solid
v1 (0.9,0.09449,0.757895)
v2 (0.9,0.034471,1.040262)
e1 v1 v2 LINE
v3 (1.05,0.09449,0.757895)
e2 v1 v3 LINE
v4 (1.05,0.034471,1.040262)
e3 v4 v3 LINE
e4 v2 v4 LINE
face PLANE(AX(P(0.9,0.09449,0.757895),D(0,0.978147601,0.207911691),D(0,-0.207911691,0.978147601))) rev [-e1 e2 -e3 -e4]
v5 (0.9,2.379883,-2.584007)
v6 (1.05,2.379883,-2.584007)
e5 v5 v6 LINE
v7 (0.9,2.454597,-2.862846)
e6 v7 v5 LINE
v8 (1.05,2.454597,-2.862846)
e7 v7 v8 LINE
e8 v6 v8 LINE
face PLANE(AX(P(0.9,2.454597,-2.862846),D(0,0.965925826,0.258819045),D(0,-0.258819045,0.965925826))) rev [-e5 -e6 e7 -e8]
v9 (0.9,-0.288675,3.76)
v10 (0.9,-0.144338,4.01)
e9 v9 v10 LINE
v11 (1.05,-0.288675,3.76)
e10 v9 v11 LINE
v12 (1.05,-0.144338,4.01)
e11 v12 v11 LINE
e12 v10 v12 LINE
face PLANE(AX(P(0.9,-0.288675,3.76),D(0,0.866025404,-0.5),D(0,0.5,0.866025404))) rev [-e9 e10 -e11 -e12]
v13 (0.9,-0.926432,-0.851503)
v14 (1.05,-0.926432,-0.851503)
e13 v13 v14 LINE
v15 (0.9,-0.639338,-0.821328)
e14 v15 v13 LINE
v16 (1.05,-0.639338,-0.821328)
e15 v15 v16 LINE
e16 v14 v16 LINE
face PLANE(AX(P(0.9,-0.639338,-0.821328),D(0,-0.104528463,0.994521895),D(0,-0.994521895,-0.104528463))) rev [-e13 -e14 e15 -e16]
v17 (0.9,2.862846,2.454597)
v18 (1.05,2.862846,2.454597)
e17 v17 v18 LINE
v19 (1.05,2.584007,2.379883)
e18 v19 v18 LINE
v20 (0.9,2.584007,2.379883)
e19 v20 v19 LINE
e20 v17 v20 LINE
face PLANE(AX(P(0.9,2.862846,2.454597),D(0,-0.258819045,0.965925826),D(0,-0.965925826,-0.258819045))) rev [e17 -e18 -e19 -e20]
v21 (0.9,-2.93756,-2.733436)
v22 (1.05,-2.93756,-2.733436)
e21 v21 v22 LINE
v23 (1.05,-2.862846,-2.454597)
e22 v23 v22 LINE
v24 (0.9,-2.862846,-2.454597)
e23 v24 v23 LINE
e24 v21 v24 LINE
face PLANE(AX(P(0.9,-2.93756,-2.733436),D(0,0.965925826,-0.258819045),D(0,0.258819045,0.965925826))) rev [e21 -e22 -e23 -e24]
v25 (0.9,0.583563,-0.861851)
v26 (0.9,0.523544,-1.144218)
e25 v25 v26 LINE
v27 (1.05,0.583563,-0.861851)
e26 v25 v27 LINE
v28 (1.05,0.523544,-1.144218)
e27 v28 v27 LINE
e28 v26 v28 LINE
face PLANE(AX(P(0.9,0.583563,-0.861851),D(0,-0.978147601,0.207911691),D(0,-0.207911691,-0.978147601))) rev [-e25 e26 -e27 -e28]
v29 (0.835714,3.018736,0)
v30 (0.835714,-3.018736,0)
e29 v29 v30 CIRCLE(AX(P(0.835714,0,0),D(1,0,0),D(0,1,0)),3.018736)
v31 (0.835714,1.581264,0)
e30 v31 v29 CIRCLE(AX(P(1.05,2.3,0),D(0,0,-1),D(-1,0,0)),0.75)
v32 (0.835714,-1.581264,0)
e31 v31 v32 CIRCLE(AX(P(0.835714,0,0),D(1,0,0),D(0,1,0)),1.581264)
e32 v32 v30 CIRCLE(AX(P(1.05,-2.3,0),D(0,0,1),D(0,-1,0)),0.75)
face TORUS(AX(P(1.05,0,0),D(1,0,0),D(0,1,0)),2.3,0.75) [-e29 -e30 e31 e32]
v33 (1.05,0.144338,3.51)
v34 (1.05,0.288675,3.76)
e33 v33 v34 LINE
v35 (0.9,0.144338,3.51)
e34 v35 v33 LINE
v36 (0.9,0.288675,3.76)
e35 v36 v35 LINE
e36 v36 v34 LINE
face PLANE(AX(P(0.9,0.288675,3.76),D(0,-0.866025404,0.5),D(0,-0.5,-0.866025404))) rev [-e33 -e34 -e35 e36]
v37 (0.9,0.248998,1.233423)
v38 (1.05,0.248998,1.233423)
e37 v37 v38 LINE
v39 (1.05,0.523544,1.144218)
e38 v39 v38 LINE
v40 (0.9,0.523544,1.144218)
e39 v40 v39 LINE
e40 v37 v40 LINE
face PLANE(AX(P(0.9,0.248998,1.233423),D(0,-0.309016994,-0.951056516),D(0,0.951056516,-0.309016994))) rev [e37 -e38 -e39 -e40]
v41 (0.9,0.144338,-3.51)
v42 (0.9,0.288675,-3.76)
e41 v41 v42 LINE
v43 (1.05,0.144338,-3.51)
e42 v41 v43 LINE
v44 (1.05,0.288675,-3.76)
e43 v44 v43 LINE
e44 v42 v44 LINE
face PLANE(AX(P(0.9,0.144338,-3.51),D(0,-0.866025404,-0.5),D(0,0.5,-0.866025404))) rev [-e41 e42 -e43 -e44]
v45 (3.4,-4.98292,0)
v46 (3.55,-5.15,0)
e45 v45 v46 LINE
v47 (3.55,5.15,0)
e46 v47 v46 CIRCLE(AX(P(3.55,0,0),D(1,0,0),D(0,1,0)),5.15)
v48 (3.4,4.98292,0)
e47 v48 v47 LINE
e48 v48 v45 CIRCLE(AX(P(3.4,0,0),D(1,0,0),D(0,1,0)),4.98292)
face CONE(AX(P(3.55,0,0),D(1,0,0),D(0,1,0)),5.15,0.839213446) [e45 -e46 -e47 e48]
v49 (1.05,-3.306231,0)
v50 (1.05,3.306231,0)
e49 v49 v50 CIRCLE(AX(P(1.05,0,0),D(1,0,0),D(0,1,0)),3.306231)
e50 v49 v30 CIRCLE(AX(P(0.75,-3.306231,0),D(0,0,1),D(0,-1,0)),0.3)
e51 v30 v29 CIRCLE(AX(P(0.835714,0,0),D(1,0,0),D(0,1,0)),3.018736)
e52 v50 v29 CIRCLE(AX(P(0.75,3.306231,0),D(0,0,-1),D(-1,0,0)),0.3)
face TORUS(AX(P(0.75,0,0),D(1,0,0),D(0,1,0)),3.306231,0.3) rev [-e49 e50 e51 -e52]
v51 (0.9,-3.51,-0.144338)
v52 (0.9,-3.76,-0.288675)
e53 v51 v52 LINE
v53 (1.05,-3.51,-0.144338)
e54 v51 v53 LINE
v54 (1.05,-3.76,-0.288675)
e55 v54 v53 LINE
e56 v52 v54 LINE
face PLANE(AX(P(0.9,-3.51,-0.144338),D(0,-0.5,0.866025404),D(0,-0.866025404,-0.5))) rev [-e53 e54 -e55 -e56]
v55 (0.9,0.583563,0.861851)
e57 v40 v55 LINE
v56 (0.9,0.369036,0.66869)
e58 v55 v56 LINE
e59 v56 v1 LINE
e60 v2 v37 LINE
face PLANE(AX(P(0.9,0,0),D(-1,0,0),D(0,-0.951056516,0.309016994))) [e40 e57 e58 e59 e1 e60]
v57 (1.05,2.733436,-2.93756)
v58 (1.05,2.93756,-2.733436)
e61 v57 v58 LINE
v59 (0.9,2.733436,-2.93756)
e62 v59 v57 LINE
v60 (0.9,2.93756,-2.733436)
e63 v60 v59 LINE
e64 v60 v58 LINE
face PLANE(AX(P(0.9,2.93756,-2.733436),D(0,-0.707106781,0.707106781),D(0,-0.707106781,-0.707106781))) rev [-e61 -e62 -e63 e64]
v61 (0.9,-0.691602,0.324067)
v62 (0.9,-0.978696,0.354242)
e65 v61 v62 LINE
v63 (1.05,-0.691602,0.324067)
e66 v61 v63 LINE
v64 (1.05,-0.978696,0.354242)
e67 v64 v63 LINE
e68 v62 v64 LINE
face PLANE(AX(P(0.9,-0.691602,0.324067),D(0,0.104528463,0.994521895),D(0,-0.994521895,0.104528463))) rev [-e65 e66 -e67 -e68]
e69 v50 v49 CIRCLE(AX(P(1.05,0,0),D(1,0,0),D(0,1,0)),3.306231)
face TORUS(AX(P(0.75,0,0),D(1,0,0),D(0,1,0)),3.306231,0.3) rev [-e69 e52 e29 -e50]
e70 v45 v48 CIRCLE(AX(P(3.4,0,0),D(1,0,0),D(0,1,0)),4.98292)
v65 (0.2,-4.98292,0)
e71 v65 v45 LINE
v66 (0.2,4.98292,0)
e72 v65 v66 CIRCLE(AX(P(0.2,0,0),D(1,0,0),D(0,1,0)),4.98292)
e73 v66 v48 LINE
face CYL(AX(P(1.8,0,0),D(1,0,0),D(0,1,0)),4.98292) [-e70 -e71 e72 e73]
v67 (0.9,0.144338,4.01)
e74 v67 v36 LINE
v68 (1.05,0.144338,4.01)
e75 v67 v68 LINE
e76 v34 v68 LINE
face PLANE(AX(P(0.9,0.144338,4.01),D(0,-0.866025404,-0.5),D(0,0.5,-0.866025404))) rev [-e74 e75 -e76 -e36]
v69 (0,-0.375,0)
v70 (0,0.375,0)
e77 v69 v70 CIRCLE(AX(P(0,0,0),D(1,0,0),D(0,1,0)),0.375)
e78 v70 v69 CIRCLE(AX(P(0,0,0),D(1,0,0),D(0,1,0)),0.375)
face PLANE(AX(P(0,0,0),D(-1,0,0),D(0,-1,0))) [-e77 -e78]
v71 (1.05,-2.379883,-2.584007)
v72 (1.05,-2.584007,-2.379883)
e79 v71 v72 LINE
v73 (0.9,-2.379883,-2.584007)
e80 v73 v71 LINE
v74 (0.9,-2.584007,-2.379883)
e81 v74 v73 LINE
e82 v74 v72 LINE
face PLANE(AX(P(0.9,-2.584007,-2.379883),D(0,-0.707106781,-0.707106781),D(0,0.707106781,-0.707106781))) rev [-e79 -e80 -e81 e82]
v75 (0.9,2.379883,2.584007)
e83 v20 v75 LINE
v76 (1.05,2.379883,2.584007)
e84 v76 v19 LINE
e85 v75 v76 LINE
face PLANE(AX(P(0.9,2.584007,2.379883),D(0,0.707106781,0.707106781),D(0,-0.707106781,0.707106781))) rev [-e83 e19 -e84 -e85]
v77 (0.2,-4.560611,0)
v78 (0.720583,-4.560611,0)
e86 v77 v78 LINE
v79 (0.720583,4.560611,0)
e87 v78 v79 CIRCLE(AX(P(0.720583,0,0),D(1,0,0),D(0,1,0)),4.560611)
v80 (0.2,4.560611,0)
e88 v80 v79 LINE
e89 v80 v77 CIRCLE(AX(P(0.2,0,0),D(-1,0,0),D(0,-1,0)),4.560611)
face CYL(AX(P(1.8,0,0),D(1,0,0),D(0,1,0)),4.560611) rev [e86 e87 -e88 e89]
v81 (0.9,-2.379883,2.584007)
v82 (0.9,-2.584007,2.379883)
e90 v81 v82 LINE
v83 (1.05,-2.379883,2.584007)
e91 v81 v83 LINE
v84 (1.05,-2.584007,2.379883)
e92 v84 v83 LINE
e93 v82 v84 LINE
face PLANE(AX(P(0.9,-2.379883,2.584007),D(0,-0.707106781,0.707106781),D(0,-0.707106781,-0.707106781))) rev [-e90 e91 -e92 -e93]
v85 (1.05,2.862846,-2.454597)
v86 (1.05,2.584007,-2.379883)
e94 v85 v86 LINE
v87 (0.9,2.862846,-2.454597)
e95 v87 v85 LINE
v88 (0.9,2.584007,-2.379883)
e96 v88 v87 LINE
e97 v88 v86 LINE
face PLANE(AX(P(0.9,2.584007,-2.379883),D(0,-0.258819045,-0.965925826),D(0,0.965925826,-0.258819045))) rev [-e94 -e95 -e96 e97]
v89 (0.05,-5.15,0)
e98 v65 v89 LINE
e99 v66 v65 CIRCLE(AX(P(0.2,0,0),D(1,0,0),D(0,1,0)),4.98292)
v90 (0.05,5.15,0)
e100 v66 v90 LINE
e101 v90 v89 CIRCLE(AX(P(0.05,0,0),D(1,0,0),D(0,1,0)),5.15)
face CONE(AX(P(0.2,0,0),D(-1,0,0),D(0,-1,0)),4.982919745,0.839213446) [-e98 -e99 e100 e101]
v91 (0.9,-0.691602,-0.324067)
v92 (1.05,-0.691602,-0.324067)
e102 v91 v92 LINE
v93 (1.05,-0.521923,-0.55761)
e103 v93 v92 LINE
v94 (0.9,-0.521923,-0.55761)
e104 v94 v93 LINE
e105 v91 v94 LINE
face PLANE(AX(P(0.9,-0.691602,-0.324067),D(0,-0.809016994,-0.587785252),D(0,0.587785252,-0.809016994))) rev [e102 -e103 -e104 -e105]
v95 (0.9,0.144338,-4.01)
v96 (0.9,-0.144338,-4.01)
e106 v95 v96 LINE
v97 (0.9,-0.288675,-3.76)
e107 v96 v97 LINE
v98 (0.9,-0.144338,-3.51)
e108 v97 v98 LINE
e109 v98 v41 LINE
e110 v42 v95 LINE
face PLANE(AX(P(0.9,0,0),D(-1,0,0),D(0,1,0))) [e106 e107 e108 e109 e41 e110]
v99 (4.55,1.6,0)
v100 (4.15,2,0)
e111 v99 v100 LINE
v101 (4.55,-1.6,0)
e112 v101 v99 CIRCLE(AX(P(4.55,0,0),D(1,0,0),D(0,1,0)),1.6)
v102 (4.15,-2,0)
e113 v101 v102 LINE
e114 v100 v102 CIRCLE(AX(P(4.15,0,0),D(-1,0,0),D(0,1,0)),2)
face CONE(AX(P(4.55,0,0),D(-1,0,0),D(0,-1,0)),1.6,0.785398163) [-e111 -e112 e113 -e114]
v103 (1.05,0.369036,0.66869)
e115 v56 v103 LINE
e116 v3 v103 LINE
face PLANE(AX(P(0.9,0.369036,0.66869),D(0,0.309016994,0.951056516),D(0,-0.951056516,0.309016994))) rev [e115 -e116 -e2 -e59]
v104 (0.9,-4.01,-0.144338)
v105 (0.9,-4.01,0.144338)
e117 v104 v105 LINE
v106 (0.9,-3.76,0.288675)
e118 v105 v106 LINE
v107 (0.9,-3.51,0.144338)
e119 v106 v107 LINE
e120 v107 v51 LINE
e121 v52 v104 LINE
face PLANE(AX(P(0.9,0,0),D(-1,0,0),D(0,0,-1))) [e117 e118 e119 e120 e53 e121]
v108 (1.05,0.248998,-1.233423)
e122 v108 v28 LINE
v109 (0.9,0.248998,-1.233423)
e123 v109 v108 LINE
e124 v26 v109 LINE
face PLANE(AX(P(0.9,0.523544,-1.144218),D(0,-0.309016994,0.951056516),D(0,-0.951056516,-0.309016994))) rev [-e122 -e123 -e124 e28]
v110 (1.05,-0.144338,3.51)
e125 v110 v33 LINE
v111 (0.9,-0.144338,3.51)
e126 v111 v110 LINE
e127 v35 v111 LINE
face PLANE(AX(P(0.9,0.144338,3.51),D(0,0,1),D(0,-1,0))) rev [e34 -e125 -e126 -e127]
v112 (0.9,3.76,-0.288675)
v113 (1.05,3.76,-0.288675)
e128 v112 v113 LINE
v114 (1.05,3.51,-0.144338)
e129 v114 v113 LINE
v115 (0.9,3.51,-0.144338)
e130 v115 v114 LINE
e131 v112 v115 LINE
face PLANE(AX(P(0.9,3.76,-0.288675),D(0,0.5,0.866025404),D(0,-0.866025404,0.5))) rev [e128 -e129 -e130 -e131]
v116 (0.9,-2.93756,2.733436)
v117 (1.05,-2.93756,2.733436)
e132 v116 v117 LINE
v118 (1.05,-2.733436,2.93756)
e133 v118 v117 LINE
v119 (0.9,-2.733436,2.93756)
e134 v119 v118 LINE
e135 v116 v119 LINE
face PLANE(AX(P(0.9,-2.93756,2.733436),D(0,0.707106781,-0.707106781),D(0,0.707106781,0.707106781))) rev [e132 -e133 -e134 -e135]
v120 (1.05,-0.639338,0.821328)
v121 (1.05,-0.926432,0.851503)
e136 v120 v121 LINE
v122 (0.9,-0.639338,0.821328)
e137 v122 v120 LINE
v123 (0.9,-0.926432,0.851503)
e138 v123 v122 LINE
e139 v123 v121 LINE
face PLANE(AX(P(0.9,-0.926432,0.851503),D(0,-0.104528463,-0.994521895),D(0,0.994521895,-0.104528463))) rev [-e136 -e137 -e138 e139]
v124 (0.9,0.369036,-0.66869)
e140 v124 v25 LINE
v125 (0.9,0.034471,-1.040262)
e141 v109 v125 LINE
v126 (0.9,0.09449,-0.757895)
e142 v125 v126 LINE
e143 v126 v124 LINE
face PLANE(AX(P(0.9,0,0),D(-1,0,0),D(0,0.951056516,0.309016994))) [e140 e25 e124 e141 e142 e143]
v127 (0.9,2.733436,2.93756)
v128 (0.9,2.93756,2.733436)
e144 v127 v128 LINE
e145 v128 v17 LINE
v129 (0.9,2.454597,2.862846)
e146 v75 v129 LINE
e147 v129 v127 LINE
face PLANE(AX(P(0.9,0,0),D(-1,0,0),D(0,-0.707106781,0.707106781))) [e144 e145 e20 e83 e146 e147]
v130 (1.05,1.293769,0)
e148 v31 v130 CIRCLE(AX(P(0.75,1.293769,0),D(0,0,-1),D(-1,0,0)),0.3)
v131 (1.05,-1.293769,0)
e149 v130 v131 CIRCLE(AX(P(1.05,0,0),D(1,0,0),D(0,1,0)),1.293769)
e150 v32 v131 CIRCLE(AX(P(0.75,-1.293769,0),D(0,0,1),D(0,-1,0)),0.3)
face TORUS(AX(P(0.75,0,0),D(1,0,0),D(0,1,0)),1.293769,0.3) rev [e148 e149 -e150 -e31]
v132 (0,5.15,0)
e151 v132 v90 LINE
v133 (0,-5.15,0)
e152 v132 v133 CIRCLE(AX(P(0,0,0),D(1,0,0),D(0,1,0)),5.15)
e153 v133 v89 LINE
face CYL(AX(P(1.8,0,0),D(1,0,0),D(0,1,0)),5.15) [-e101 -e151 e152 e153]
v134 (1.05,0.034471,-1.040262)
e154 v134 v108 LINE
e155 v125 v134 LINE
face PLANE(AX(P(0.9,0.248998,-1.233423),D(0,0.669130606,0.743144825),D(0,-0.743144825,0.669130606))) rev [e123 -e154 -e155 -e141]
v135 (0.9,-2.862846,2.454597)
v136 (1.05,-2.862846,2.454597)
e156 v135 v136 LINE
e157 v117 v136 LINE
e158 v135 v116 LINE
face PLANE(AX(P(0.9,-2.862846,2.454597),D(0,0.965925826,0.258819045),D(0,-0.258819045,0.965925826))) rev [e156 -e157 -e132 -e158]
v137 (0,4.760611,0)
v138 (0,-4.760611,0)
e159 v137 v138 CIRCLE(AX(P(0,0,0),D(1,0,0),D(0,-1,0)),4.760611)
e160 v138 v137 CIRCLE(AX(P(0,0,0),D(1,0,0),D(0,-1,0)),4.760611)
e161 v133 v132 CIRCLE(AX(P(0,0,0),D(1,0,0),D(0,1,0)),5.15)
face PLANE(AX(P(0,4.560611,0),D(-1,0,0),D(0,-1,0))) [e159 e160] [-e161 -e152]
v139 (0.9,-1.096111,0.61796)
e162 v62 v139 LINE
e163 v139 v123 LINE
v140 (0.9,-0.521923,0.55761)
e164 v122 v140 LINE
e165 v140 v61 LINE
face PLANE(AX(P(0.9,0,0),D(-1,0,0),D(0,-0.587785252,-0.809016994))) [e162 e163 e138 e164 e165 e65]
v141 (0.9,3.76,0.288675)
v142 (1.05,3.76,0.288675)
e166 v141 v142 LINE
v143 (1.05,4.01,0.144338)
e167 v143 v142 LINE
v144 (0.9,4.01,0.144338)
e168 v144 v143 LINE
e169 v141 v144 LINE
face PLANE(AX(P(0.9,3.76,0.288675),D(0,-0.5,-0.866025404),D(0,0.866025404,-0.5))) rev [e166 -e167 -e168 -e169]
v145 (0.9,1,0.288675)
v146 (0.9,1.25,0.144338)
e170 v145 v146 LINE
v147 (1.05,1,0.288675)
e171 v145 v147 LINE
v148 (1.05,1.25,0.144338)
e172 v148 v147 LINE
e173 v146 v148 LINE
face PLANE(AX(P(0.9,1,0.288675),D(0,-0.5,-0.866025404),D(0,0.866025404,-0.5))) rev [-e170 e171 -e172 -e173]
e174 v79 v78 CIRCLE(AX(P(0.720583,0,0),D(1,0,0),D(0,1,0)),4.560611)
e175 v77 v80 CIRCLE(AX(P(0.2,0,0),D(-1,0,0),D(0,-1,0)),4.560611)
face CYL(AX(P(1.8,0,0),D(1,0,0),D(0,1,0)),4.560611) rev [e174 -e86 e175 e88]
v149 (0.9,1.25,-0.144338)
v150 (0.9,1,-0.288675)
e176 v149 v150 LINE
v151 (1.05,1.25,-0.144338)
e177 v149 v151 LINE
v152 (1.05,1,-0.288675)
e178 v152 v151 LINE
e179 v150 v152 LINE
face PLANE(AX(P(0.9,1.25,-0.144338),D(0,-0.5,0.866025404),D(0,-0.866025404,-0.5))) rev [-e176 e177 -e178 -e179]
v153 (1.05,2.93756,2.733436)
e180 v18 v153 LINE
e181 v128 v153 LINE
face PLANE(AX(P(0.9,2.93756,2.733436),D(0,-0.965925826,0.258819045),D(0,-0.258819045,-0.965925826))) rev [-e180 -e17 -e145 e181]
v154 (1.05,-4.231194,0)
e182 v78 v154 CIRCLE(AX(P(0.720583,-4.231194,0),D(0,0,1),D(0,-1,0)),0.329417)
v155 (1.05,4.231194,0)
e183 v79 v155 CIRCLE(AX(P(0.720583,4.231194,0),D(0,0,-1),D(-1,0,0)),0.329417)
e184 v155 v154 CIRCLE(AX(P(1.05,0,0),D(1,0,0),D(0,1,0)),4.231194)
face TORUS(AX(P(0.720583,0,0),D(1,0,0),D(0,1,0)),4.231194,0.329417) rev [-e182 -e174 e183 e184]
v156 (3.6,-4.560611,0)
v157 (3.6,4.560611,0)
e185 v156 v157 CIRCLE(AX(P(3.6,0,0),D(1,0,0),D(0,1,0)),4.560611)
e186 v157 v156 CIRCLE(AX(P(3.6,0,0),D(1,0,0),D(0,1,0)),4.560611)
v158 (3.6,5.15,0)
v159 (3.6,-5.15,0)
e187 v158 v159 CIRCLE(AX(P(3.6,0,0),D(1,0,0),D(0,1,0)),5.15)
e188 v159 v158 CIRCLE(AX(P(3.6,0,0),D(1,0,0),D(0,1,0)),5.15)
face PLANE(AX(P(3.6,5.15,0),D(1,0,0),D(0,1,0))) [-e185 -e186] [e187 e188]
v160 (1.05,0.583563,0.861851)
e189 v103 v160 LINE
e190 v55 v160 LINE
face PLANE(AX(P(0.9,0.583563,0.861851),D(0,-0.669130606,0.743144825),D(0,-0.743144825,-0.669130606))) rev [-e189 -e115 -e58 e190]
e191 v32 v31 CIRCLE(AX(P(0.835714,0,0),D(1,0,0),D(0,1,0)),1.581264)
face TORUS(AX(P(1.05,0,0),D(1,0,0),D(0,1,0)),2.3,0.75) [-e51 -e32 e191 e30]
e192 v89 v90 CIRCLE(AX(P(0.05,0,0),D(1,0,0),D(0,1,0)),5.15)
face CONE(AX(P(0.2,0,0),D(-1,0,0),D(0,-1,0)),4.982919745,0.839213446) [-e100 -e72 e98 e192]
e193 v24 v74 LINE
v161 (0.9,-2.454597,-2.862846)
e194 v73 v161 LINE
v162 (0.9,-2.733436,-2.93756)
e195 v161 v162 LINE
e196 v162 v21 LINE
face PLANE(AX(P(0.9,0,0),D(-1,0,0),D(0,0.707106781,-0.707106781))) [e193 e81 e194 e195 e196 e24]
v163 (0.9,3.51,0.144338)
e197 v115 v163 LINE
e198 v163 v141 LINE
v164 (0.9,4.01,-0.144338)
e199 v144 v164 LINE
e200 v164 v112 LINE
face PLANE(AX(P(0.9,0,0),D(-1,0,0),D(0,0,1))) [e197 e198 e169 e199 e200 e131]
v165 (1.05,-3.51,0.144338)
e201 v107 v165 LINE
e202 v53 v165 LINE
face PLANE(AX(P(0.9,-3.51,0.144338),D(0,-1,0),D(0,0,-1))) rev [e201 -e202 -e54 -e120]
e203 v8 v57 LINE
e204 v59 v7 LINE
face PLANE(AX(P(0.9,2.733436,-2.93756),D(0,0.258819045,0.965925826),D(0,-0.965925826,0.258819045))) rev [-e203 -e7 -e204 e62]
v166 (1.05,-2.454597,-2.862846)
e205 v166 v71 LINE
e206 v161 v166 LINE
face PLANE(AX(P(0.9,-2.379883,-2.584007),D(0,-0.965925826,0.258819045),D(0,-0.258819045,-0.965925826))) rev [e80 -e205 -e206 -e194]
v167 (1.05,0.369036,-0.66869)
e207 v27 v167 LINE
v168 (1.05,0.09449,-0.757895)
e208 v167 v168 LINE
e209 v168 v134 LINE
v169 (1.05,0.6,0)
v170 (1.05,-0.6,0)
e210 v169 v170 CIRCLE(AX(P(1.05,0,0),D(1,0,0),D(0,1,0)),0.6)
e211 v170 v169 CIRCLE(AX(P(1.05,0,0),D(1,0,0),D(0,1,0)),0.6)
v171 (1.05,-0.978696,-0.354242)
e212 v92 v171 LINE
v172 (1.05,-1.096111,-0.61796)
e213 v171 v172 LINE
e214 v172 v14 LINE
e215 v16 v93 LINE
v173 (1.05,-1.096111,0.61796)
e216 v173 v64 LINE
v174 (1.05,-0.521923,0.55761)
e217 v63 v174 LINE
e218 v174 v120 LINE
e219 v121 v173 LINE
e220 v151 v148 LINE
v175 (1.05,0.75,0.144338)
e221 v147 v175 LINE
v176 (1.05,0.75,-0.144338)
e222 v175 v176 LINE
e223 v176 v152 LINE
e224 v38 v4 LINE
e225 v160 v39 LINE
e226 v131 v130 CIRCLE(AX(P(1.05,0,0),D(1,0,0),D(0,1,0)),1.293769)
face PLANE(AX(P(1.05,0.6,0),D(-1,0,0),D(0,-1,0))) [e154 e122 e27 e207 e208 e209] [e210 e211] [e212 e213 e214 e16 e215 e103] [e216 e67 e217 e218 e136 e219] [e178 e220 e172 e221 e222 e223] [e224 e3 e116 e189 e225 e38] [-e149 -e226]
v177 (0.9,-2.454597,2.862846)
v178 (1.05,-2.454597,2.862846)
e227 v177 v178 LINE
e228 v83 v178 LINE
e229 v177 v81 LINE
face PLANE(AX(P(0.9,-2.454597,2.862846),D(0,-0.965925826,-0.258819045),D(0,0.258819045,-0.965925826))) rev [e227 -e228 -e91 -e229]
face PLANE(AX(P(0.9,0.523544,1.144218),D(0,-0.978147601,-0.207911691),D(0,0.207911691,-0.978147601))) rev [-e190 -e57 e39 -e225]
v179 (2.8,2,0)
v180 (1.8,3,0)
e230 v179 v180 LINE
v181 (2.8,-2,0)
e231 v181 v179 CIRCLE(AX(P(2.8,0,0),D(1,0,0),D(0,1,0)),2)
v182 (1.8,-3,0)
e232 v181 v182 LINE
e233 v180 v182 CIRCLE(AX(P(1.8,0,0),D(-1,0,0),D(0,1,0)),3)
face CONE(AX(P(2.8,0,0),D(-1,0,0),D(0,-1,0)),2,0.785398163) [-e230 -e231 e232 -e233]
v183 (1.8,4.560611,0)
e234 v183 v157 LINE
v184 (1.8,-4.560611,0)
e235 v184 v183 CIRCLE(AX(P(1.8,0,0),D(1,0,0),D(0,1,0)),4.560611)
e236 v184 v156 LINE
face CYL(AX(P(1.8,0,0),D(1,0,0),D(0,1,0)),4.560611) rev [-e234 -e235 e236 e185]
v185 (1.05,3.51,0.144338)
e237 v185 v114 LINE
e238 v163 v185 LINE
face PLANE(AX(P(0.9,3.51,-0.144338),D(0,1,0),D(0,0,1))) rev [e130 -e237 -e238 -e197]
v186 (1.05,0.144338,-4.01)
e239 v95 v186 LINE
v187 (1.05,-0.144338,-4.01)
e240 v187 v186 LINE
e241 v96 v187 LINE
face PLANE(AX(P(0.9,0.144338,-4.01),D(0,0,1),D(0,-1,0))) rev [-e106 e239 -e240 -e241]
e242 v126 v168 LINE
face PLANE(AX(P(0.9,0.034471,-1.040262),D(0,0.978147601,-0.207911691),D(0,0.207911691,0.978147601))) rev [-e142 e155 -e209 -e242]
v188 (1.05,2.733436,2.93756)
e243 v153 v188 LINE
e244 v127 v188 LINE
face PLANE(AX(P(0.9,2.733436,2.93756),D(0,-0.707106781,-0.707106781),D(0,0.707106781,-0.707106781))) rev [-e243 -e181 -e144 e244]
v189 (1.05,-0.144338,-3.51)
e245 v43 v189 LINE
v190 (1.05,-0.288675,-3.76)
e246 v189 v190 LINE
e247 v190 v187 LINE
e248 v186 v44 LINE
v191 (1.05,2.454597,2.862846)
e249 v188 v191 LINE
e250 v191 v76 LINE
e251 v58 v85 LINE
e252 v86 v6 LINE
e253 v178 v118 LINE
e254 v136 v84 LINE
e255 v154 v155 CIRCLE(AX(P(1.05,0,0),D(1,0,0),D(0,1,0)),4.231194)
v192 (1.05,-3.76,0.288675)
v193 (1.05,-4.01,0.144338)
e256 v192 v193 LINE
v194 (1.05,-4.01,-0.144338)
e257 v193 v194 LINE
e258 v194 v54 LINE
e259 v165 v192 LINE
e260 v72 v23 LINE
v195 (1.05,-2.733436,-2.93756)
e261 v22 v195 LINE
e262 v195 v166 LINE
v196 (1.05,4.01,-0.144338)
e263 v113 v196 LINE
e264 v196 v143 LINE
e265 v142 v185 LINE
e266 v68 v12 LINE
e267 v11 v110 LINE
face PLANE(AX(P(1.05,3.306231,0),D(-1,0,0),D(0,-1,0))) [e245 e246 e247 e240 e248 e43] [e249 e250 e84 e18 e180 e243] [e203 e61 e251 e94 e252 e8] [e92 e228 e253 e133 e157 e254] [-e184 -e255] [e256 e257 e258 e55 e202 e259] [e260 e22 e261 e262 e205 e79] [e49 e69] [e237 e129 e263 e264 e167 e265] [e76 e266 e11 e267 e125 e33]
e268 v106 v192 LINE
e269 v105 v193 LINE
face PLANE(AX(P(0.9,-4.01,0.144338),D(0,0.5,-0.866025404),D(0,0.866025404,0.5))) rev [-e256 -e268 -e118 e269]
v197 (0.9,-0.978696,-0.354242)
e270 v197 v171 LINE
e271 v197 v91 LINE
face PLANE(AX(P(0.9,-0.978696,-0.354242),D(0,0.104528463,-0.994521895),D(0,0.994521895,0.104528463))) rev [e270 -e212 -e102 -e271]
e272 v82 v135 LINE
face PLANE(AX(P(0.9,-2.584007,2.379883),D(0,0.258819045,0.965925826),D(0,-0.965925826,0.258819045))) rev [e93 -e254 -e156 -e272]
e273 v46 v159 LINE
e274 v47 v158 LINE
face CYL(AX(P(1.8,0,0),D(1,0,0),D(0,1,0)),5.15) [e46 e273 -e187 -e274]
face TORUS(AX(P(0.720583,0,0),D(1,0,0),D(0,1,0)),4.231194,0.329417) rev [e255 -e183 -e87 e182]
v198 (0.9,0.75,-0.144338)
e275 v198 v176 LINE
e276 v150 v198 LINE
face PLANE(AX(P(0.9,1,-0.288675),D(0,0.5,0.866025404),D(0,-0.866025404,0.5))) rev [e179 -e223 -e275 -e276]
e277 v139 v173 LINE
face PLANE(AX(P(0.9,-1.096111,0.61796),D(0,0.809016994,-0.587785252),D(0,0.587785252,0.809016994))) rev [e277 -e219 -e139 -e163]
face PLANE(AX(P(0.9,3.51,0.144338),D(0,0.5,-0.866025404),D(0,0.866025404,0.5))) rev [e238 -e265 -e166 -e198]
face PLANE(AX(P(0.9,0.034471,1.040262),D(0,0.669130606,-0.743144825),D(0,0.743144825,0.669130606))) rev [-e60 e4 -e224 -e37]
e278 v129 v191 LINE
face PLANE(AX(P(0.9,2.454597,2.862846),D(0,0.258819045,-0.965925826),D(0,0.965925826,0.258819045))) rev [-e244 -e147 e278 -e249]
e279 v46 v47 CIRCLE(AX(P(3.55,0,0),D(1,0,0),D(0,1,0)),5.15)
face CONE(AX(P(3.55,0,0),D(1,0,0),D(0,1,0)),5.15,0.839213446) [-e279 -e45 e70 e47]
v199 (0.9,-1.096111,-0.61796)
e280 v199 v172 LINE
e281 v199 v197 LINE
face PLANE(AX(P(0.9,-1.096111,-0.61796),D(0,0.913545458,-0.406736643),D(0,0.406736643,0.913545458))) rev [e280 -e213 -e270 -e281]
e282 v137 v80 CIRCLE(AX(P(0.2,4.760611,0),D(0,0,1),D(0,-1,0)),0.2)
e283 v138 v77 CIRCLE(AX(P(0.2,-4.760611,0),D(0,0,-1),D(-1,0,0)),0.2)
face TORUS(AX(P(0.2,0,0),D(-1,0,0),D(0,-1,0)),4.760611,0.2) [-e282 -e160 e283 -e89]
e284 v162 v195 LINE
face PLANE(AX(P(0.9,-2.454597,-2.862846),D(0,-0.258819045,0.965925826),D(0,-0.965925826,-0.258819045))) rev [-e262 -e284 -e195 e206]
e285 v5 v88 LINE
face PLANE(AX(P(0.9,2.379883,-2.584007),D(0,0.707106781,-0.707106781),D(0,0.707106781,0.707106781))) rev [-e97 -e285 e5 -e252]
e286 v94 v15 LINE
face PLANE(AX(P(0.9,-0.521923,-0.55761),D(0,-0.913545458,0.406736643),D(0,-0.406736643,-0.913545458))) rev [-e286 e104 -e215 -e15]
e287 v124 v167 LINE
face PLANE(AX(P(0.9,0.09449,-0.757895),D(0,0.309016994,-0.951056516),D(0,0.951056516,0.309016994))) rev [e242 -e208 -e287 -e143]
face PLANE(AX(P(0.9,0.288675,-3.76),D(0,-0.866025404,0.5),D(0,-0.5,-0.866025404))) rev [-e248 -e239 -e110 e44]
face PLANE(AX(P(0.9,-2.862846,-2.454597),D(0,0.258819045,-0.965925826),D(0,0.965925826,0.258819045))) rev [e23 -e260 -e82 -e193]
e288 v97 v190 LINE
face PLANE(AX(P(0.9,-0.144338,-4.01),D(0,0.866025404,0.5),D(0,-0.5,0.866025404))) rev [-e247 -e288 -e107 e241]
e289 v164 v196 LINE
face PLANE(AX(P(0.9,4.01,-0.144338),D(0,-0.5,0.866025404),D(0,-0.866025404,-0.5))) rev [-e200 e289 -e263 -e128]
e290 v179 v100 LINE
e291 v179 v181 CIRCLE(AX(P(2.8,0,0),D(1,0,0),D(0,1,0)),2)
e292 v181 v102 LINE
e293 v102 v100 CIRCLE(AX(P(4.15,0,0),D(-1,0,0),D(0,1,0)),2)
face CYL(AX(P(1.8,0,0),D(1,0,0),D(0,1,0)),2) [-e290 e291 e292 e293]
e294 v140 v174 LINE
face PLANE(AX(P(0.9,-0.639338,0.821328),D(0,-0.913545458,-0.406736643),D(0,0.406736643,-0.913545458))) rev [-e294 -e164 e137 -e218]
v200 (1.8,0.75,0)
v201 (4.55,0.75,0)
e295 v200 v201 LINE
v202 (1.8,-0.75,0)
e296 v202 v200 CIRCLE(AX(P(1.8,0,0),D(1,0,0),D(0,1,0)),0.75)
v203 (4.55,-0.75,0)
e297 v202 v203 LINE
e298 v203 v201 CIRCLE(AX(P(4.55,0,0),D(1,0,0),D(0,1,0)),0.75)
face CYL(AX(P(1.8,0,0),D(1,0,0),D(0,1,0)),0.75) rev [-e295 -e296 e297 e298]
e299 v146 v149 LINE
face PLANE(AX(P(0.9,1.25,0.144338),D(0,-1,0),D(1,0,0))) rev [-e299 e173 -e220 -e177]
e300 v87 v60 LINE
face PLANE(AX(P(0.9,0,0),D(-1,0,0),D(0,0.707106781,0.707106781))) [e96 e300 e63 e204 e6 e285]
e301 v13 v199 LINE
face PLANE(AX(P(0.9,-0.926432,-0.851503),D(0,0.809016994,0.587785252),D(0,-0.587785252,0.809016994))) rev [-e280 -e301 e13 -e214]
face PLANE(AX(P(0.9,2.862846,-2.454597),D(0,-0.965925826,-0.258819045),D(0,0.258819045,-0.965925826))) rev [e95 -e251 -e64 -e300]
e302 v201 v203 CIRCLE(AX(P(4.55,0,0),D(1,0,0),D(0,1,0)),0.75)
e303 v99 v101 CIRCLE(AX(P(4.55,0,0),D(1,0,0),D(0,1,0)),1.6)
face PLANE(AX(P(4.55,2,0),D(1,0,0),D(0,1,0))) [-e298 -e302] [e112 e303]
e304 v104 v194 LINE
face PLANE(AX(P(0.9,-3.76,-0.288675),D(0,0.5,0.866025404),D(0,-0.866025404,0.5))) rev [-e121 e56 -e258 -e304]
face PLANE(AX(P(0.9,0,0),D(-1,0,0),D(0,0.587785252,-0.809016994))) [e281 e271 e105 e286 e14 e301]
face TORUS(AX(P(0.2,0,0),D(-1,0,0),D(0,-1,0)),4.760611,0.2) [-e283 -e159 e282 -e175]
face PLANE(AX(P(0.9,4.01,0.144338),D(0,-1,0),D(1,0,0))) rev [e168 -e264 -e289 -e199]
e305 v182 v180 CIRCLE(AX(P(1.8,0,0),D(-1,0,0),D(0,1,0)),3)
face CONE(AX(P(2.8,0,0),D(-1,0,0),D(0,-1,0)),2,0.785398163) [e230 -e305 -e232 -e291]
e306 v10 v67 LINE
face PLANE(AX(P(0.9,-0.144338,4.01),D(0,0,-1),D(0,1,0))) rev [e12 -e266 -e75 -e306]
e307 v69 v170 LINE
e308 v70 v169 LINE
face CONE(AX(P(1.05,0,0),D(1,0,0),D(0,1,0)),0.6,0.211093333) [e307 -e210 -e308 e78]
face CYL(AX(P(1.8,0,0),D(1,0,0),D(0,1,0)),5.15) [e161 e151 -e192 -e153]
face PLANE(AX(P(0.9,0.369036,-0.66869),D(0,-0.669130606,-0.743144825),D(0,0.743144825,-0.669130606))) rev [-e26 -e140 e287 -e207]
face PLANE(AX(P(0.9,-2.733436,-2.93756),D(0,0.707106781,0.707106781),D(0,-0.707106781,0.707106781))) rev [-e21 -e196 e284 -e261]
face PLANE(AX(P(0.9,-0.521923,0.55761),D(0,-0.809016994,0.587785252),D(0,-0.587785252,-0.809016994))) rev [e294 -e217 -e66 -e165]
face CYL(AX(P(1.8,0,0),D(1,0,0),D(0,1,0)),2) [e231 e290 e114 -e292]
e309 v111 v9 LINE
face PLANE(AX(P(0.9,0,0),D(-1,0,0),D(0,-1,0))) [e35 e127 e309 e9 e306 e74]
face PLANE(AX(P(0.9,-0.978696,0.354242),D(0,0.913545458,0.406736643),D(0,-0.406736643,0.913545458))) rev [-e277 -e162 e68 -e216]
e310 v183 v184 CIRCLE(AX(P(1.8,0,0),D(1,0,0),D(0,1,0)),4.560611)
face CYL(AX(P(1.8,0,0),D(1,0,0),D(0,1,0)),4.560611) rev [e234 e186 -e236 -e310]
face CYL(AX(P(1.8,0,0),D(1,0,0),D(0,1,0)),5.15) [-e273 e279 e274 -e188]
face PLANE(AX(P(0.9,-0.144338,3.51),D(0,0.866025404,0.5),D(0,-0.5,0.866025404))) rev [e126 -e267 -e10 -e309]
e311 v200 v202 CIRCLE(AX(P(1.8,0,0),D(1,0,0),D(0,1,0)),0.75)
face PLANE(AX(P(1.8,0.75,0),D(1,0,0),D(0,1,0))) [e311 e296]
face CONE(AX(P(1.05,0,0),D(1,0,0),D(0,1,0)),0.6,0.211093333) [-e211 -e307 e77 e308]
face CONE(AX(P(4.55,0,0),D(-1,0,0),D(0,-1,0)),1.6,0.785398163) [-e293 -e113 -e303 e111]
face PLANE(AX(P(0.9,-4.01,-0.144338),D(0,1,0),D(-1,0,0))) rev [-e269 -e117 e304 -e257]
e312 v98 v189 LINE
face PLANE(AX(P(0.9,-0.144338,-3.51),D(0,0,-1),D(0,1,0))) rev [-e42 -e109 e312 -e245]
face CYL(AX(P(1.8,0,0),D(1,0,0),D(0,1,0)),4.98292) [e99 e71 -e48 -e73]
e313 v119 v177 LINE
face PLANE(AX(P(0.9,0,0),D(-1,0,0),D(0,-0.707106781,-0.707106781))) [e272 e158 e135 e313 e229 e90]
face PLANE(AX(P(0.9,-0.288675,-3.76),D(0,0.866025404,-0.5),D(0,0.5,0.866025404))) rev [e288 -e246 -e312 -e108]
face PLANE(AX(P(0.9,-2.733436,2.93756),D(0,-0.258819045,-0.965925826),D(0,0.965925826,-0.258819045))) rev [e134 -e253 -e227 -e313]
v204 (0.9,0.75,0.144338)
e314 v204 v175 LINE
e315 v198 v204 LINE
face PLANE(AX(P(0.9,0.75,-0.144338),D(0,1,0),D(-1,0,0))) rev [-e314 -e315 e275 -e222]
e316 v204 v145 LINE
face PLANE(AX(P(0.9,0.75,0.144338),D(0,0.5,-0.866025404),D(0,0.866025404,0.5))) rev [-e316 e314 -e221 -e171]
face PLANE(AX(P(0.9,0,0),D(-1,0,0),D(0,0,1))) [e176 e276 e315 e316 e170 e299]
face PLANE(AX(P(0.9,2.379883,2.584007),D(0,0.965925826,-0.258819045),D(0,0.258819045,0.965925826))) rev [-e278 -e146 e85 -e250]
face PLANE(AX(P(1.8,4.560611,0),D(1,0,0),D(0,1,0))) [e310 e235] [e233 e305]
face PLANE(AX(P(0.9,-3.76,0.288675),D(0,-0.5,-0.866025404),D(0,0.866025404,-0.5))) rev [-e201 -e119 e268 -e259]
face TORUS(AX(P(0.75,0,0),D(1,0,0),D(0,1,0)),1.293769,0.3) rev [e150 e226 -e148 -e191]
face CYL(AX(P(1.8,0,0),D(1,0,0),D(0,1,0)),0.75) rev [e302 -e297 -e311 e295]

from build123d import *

# Parameters (mm, degrees)
CHAMFER1_SIZE       = 0.4
FILLET1_R           = 0.2
CHAMFER2_SIZE       = 1
BOSS_EXTRUDE1_DEPTH = 0.15
CIRPATTERN1_COUNT   = 8
BOSS_EXTRUDE2_DEPTH = 0.15
CIRPATTERN2_COUNT   = 5


with BuildPart() as part:
    # Sketch1 → Revolve1 (revolve)
    with BuildSketch(Plane.XY):
        with BuildLine():
            Line((0, 0), (0, 0.375))
            Line((0, 0.375), (1.05, 0.6))
            Line((1.05, 0.6), (1.05, 1.29376941))
            ThreePointArc((1.05, 1.29376941), (0.990535118, 1.473053702), (0.835714286, 1.581263864))
            ThreePointArc((0.835714286, 1.581263864), (0.3, 2.3), (0.835714286, 3.018736136))
            ThreePointArc((0.835714286, 3.018736136), (0.990535118, 3.126946298), (1.05, 3.30623059))
            Line((1.05, 3.30623059), (1.05, 4.231193843))
            ThreePointArc((1.05, 4.231193843), (0.953516085, 4.46412662), (0.720583307, 4.560610535))
            Line((0.720583307, 4.560610535), (0, 4.560610535))
            Line((0, 4.560610535), (0, 5.15))
            Line((0, 5.15), (0.05, 5.15))
            Line((0.05, 5.15), (0.2, 4.982919745))
            Line((0.2, 4.982919745), (3.4, 4.982919745))
            Line((3.4, 4.982919745), (3.55, 5.15))
            Line((3.55, 5.15), (3.6, 5.15))
            Line((3.6, 5.15), (3.6, 4.560610535))
            Line((3.6, 4.560610535), (1.8, 4.560610535))
            Line((1.8, 4.560610535), (1.8, 2))
            Line((1.8, 2), (4.55, 2))
            Line((4.55, 2), (4.55, 0.75))
            Line((4.55, 0.75), (1.8, 0.75))
            Line((1.8, 0.75), (1.8, 0))
            Line((1.8, 0), (0, 0))
        make_face()
    revolve(axis=Axis((1.8, 0, 0), (-1, 0, 0)))

    # Chamfer1
    chamfer1_edges = [part.edges().sort_by_distance(p)[0] for p in [
        (4.55, -2, 0),
    ]]
    chamfer(chamfer1_edges, length=CHAMFER1_SIZE)

    # Fillet1
    fillet1_edges = [part.edges().sort_by_distance(p)[0] for p in [
        (0, -4.560610535, 0),
    ]]
    fillet(fillet1_edges, radius=FILLET1_R)

    # Chamfer2
    chamfer2_edges = [part.edges().sort_by_distance(p)[0] for p in [
        (1.8, -2, 0),
    ]]
    chamfer(chamfer2_edges, length=CHAMFER2_SIZE)

    # Sketch2 → Boss-Extrude1 (add, symmetric)
    with BuildSketch(Plane.ZY.offset(-1.05)):
        Polygon((0.288675135, 3.76), (0.144337567, 4.01), (-0.144337567, 4.01), (-0.288675135, 3.76), (-0.144337567, 3.51), (0.144337567, 3.51), align=None)
    boss_extrude1 = extrude(amount=BOSS_EXTRUDE1_DEPTH, both=True)

    # CirPattern1: Boss-Extrude1 ×8 about axis
    cirpattern1_axis = Axis((0, 0, 0), (1, 0, 0))
    for i in range(1, CIRPATTERN1_COUNT):
        add(boss_extrude1.rotate(cirpattern1_axis, i * 360 / CIRPATTERN1_COUNT))

    # Sketch3 → Boss-Extrude2 (add, symmetric)
    with BuildSketch(Plane.ZY.offset(-1.05)):
        Polygon((0.288675135, 1), (0.144337567, 1.25), (-0.144337567, 1.25), (-0.288675135, 1), (-0.144337567, 0.75), (0.144337567, 0.75), align=None)
    boss_extrude2 = extrude(amount=BOSS_EXTRUDE2_DEPTH, both=True)

    # CirPattern2: Boss-Extrude2 ×5 about axis
    cirpattern2_axis = Axis((0, 0, 0), (1, 0, 0))
    for i in range(1, CIRPATTERN2_COUNT):
        add(boss_extrude2.rotate(cirpattern2_axis, i * 360 / CIRPATTERN2_COUNT))


solid = part.part
